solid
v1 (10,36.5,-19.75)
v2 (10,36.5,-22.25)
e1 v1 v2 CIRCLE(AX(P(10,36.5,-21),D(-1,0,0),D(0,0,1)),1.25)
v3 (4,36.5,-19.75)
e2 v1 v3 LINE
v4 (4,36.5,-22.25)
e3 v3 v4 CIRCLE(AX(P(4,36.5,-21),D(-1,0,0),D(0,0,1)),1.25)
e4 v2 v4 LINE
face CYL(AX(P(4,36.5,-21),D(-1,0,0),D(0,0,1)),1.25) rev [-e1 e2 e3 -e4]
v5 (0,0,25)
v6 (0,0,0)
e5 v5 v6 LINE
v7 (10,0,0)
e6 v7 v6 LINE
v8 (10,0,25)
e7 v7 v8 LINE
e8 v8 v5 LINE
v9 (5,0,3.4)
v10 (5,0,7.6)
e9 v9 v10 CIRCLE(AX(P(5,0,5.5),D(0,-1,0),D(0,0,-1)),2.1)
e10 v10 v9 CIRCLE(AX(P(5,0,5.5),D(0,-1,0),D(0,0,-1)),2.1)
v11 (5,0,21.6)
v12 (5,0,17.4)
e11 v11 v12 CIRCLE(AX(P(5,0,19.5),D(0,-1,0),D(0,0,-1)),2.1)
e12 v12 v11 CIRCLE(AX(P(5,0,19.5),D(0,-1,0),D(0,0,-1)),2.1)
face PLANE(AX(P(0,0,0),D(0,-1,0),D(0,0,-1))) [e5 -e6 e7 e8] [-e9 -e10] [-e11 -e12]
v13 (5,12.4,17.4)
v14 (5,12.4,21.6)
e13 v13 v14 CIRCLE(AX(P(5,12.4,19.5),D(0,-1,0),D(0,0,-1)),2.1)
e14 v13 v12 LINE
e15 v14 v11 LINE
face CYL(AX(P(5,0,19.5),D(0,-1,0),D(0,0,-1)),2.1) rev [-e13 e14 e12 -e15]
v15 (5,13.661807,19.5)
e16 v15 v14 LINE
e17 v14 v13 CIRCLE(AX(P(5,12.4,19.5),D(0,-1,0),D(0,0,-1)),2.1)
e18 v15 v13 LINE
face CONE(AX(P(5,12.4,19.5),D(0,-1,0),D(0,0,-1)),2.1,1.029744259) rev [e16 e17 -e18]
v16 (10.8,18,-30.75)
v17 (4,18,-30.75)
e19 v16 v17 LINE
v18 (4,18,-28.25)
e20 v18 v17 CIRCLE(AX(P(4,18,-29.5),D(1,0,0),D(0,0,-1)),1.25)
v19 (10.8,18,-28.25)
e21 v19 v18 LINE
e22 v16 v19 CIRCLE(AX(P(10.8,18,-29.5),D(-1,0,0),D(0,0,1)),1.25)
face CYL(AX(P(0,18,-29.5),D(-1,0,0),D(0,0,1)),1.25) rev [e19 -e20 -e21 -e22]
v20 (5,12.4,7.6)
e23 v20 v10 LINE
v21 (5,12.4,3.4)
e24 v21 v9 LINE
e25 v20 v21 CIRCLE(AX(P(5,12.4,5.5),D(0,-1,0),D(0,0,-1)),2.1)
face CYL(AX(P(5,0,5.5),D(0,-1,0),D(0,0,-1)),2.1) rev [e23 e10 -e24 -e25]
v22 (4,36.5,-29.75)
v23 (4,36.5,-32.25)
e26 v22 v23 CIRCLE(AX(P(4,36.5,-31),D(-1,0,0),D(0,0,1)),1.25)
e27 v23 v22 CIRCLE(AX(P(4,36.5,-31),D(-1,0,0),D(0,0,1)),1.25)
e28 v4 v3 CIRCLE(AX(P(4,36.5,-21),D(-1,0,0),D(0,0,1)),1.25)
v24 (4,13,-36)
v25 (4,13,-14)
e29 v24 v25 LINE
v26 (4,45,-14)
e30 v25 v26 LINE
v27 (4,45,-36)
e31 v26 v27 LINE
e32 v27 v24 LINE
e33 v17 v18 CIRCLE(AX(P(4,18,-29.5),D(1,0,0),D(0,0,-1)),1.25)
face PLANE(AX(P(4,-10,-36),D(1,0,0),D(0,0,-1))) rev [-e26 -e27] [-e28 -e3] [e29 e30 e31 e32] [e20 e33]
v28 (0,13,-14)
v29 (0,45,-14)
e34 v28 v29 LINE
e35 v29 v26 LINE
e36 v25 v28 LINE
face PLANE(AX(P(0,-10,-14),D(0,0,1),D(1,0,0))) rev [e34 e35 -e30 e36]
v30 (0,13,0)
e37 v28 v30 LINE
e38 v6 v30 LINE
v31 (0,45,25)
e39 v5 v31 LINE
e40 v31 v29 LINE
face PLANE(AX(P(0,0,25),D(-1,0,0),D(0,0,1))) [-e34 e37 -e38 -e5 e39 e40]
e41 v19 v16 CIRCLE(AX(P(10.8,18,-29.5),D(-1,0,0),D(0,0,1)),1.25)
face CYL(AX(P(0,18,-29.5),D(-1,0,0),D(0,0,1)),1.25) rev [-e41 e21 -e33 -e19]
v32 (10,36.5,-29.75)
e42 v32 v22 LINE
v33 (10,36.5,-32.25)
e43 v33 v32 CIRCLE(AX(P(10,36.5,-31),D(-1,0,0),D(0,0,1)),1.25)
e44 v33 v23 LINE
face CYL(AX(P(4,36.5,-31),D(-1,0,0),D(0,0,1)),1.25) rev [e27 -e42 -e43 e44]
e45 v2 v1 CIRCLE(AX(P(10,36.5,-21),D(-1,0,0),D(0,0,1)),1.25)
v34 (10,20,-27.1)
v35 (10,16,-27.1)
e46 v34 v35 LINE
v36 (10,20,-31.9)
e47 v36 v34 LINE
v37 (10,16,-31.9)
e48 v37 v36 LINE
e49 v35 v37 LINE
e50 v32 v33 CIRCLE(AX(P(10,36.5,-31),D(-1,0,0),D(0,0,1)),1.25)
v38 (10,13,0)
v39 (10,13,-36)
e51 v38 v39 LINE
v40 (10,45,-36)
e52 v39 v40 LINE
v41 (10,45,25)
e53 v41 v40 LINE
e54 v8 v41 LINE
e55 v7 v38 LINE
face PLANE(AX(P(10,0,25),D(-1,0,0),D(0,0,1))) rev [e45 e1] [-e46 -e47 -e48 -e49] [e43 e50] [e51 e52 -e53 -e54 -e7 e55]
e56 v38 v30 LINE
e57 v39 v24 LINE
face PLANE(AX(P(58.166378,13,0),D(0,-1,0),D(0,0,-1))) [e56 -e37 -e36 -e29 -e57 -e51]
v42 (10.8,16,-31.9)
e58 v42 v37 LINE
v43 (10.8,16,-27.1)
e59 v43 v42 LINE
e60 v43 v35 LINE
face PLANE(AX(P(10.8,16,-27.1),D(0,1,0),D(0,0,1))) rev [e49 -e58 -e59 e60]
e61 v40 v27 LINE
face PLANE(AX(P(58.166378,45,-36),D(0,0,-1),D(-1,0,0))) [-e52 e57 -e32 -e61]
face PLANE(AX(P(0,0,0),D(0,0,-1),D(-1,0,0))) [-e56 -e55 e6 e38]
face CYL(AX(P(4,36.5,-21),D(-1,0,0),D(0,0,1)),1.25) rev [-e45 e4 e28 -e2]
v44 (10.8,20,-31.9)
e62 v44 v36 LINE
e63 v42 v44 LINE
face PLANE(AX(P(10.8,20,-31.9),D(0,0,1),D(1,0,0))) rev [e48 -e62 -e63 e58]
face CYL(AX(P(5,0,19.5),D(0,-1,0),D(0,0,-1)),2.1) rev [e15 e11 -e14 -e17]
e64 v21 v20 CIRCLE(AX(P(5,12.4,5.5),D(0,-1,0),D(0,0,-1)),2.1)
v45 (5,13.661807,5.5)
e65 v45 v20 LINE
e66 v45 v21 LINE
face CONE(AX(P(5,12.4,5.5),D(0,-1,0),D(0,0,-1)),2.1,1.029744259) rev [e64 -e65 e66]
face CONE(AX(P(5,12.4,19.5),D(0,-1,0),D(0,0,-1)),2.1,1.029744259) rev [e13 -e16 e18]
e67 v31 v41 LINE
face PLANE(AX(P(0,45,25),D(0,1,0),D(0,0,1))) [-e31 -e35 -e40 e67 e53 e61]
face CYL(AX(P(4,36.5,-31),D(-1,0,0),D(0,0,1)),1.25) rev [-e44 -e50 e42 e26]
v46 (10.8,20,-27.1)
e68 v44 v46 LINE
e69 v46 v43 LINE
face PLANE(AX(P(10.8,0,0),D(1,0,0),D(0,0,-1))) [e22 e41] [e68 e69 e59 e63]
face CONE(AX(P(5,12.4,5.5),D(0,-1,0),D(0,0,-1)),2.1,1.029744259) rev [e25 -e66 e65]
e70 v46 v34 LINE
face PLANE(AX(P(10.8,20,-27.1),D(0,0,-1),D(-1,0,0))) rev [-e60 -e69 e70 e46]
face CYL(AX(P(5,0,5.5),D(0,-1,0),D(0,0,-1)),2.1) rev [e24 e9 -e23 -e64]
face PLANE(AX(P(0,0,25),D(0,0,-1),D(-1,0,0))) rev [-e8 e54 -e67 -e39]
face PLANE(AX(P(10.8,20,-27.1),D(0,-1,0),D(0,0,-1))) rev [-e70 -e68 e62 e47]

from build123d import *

# Parameters (mm, degrees)
EXTRUDE_THIN1_DEPTH   = 25
SKETCH2_W             = 36
SKETCH2_H             = 32
BOSS_EXTRUDE1_DEPTH   = 10
SKETCH5_W             = 4
SKETCH5_H             = 22
CUT_EXTRUDE1_DEPTH    = 68.424031324
SKETCH6_W             = 55.512258346
SKETCH6_H             = 44.910131752
CUT_EXTRUDE2_DEPTH    = 10
M5_TAPPED_HOLE1_D     = 4.2
M5_TAPPED_HOLE1_DEPTH = 12.4
M5_TAPPED_HOLE1_TIP   = 1.2618073
M3_TAPPED_HOLE1_D     = 2.5
SKETCH11_W            = 4.8
SKETCH11_H            = 4
BOSS_EXTRUDE2_DEPTH   = 0.8
M3_TAPPED_HOLE2_D     = 2.5


with BuildPart() as part:
    # Sketch1 → Extrude-Thin1 (new body)
    with BuildSketch(Plane.XY):
        Polygon((-15, 0), (0, 0), (0, 45), (10, 45), (10, -10), (-15, -10), align=None)
    extrude(amount=EXTRUDE_THIN1_DEPTH)

    # Sketch2 → Boss-Extrude1 (add)
    with BuildSketch(Plane.ZY):
        with Locations((-18, 29)):
            Rectangle(SKETCH2_W, SKETCH2_H)
    extrude(amount=-BOSS_EXTRUDE1_DEPTH)

    # Sketch5 → Cut-Extrude1 (cut, through all)
    with BuildSketch(Plane(origin=(0, 45, 0), x_dir=(1, 0, 0), z_dir=(0, 1, 0))):
        with Locations((2, 25)):
            Rectangle(SKETCH5_W, SKETCH5_H)
    extrude(amount=-CUT_EXTRUDE1_DEPTH, mode=Mode.SUBTRACT)

    # Sketch6 → Cut-Extrude2 (cut)
    with BuildSketch(Plane.XZ.offset(10)):
        with Locations((-2.5, 9.73543964)):
            Rectangle(SKETCH6_W, SKETCH6_H)
    extrude(amount=-CUT_EXTRUDE2_DEPTH, mode=Mode.SUBTRACT)

    # M5 Tapped Hole1
    with Locations(Plane(origin=(0, 0, 0), x_dir=(-1, 0, 0), z_dir=(0, -1, 0))):
        with Locations((-5, -5.5), (-5, -19.5)):
            Hole(M5_TAPPED_HOLE1_D / 2, depth=M5_TAPPED_HOLE1_DEPTH)
            with Locations((0, 0, -(M5_TAPPED_HOLE1_DEPTH + M5_TAPPED_HOLE1_TIP / 2))):  # 118° drill point
                Cone(0, M5_TAPPED_HOLE1_D / 2, M5_TAPPED_HOLE1_TIP, mode=Mode.SUBTRACT)

    # M3 Tapped Hole1 (through all)
    with Locations(Plane.ZY.offset(-4)):
        with Locations((-31, 36.5), (-21, 36.5)):
            Hole(M3_TAPPED_HOLE1_D / 2)

    # Sketch11 → Boss-Extrude2 (add)
    with BuildSketch(Plane(origin=(10, 0, 0), x_dir=(0, 0, -1), z_dir=(1, 0, 0))):
        with Locations((29.5, 18)):
            Rectangle(SKETCH11_W, SKETCH11_H)
    extrude(amount=BOSS_EXTRUDE2_DEPTH)

    # M3 Tapped Hole2 (through all)
    with Locations(Plane.ZY):
        with Locations((-29.5, 18)):
            Hole(M3_TAPPED_HOLE2_D / 2)


solid = part.part
